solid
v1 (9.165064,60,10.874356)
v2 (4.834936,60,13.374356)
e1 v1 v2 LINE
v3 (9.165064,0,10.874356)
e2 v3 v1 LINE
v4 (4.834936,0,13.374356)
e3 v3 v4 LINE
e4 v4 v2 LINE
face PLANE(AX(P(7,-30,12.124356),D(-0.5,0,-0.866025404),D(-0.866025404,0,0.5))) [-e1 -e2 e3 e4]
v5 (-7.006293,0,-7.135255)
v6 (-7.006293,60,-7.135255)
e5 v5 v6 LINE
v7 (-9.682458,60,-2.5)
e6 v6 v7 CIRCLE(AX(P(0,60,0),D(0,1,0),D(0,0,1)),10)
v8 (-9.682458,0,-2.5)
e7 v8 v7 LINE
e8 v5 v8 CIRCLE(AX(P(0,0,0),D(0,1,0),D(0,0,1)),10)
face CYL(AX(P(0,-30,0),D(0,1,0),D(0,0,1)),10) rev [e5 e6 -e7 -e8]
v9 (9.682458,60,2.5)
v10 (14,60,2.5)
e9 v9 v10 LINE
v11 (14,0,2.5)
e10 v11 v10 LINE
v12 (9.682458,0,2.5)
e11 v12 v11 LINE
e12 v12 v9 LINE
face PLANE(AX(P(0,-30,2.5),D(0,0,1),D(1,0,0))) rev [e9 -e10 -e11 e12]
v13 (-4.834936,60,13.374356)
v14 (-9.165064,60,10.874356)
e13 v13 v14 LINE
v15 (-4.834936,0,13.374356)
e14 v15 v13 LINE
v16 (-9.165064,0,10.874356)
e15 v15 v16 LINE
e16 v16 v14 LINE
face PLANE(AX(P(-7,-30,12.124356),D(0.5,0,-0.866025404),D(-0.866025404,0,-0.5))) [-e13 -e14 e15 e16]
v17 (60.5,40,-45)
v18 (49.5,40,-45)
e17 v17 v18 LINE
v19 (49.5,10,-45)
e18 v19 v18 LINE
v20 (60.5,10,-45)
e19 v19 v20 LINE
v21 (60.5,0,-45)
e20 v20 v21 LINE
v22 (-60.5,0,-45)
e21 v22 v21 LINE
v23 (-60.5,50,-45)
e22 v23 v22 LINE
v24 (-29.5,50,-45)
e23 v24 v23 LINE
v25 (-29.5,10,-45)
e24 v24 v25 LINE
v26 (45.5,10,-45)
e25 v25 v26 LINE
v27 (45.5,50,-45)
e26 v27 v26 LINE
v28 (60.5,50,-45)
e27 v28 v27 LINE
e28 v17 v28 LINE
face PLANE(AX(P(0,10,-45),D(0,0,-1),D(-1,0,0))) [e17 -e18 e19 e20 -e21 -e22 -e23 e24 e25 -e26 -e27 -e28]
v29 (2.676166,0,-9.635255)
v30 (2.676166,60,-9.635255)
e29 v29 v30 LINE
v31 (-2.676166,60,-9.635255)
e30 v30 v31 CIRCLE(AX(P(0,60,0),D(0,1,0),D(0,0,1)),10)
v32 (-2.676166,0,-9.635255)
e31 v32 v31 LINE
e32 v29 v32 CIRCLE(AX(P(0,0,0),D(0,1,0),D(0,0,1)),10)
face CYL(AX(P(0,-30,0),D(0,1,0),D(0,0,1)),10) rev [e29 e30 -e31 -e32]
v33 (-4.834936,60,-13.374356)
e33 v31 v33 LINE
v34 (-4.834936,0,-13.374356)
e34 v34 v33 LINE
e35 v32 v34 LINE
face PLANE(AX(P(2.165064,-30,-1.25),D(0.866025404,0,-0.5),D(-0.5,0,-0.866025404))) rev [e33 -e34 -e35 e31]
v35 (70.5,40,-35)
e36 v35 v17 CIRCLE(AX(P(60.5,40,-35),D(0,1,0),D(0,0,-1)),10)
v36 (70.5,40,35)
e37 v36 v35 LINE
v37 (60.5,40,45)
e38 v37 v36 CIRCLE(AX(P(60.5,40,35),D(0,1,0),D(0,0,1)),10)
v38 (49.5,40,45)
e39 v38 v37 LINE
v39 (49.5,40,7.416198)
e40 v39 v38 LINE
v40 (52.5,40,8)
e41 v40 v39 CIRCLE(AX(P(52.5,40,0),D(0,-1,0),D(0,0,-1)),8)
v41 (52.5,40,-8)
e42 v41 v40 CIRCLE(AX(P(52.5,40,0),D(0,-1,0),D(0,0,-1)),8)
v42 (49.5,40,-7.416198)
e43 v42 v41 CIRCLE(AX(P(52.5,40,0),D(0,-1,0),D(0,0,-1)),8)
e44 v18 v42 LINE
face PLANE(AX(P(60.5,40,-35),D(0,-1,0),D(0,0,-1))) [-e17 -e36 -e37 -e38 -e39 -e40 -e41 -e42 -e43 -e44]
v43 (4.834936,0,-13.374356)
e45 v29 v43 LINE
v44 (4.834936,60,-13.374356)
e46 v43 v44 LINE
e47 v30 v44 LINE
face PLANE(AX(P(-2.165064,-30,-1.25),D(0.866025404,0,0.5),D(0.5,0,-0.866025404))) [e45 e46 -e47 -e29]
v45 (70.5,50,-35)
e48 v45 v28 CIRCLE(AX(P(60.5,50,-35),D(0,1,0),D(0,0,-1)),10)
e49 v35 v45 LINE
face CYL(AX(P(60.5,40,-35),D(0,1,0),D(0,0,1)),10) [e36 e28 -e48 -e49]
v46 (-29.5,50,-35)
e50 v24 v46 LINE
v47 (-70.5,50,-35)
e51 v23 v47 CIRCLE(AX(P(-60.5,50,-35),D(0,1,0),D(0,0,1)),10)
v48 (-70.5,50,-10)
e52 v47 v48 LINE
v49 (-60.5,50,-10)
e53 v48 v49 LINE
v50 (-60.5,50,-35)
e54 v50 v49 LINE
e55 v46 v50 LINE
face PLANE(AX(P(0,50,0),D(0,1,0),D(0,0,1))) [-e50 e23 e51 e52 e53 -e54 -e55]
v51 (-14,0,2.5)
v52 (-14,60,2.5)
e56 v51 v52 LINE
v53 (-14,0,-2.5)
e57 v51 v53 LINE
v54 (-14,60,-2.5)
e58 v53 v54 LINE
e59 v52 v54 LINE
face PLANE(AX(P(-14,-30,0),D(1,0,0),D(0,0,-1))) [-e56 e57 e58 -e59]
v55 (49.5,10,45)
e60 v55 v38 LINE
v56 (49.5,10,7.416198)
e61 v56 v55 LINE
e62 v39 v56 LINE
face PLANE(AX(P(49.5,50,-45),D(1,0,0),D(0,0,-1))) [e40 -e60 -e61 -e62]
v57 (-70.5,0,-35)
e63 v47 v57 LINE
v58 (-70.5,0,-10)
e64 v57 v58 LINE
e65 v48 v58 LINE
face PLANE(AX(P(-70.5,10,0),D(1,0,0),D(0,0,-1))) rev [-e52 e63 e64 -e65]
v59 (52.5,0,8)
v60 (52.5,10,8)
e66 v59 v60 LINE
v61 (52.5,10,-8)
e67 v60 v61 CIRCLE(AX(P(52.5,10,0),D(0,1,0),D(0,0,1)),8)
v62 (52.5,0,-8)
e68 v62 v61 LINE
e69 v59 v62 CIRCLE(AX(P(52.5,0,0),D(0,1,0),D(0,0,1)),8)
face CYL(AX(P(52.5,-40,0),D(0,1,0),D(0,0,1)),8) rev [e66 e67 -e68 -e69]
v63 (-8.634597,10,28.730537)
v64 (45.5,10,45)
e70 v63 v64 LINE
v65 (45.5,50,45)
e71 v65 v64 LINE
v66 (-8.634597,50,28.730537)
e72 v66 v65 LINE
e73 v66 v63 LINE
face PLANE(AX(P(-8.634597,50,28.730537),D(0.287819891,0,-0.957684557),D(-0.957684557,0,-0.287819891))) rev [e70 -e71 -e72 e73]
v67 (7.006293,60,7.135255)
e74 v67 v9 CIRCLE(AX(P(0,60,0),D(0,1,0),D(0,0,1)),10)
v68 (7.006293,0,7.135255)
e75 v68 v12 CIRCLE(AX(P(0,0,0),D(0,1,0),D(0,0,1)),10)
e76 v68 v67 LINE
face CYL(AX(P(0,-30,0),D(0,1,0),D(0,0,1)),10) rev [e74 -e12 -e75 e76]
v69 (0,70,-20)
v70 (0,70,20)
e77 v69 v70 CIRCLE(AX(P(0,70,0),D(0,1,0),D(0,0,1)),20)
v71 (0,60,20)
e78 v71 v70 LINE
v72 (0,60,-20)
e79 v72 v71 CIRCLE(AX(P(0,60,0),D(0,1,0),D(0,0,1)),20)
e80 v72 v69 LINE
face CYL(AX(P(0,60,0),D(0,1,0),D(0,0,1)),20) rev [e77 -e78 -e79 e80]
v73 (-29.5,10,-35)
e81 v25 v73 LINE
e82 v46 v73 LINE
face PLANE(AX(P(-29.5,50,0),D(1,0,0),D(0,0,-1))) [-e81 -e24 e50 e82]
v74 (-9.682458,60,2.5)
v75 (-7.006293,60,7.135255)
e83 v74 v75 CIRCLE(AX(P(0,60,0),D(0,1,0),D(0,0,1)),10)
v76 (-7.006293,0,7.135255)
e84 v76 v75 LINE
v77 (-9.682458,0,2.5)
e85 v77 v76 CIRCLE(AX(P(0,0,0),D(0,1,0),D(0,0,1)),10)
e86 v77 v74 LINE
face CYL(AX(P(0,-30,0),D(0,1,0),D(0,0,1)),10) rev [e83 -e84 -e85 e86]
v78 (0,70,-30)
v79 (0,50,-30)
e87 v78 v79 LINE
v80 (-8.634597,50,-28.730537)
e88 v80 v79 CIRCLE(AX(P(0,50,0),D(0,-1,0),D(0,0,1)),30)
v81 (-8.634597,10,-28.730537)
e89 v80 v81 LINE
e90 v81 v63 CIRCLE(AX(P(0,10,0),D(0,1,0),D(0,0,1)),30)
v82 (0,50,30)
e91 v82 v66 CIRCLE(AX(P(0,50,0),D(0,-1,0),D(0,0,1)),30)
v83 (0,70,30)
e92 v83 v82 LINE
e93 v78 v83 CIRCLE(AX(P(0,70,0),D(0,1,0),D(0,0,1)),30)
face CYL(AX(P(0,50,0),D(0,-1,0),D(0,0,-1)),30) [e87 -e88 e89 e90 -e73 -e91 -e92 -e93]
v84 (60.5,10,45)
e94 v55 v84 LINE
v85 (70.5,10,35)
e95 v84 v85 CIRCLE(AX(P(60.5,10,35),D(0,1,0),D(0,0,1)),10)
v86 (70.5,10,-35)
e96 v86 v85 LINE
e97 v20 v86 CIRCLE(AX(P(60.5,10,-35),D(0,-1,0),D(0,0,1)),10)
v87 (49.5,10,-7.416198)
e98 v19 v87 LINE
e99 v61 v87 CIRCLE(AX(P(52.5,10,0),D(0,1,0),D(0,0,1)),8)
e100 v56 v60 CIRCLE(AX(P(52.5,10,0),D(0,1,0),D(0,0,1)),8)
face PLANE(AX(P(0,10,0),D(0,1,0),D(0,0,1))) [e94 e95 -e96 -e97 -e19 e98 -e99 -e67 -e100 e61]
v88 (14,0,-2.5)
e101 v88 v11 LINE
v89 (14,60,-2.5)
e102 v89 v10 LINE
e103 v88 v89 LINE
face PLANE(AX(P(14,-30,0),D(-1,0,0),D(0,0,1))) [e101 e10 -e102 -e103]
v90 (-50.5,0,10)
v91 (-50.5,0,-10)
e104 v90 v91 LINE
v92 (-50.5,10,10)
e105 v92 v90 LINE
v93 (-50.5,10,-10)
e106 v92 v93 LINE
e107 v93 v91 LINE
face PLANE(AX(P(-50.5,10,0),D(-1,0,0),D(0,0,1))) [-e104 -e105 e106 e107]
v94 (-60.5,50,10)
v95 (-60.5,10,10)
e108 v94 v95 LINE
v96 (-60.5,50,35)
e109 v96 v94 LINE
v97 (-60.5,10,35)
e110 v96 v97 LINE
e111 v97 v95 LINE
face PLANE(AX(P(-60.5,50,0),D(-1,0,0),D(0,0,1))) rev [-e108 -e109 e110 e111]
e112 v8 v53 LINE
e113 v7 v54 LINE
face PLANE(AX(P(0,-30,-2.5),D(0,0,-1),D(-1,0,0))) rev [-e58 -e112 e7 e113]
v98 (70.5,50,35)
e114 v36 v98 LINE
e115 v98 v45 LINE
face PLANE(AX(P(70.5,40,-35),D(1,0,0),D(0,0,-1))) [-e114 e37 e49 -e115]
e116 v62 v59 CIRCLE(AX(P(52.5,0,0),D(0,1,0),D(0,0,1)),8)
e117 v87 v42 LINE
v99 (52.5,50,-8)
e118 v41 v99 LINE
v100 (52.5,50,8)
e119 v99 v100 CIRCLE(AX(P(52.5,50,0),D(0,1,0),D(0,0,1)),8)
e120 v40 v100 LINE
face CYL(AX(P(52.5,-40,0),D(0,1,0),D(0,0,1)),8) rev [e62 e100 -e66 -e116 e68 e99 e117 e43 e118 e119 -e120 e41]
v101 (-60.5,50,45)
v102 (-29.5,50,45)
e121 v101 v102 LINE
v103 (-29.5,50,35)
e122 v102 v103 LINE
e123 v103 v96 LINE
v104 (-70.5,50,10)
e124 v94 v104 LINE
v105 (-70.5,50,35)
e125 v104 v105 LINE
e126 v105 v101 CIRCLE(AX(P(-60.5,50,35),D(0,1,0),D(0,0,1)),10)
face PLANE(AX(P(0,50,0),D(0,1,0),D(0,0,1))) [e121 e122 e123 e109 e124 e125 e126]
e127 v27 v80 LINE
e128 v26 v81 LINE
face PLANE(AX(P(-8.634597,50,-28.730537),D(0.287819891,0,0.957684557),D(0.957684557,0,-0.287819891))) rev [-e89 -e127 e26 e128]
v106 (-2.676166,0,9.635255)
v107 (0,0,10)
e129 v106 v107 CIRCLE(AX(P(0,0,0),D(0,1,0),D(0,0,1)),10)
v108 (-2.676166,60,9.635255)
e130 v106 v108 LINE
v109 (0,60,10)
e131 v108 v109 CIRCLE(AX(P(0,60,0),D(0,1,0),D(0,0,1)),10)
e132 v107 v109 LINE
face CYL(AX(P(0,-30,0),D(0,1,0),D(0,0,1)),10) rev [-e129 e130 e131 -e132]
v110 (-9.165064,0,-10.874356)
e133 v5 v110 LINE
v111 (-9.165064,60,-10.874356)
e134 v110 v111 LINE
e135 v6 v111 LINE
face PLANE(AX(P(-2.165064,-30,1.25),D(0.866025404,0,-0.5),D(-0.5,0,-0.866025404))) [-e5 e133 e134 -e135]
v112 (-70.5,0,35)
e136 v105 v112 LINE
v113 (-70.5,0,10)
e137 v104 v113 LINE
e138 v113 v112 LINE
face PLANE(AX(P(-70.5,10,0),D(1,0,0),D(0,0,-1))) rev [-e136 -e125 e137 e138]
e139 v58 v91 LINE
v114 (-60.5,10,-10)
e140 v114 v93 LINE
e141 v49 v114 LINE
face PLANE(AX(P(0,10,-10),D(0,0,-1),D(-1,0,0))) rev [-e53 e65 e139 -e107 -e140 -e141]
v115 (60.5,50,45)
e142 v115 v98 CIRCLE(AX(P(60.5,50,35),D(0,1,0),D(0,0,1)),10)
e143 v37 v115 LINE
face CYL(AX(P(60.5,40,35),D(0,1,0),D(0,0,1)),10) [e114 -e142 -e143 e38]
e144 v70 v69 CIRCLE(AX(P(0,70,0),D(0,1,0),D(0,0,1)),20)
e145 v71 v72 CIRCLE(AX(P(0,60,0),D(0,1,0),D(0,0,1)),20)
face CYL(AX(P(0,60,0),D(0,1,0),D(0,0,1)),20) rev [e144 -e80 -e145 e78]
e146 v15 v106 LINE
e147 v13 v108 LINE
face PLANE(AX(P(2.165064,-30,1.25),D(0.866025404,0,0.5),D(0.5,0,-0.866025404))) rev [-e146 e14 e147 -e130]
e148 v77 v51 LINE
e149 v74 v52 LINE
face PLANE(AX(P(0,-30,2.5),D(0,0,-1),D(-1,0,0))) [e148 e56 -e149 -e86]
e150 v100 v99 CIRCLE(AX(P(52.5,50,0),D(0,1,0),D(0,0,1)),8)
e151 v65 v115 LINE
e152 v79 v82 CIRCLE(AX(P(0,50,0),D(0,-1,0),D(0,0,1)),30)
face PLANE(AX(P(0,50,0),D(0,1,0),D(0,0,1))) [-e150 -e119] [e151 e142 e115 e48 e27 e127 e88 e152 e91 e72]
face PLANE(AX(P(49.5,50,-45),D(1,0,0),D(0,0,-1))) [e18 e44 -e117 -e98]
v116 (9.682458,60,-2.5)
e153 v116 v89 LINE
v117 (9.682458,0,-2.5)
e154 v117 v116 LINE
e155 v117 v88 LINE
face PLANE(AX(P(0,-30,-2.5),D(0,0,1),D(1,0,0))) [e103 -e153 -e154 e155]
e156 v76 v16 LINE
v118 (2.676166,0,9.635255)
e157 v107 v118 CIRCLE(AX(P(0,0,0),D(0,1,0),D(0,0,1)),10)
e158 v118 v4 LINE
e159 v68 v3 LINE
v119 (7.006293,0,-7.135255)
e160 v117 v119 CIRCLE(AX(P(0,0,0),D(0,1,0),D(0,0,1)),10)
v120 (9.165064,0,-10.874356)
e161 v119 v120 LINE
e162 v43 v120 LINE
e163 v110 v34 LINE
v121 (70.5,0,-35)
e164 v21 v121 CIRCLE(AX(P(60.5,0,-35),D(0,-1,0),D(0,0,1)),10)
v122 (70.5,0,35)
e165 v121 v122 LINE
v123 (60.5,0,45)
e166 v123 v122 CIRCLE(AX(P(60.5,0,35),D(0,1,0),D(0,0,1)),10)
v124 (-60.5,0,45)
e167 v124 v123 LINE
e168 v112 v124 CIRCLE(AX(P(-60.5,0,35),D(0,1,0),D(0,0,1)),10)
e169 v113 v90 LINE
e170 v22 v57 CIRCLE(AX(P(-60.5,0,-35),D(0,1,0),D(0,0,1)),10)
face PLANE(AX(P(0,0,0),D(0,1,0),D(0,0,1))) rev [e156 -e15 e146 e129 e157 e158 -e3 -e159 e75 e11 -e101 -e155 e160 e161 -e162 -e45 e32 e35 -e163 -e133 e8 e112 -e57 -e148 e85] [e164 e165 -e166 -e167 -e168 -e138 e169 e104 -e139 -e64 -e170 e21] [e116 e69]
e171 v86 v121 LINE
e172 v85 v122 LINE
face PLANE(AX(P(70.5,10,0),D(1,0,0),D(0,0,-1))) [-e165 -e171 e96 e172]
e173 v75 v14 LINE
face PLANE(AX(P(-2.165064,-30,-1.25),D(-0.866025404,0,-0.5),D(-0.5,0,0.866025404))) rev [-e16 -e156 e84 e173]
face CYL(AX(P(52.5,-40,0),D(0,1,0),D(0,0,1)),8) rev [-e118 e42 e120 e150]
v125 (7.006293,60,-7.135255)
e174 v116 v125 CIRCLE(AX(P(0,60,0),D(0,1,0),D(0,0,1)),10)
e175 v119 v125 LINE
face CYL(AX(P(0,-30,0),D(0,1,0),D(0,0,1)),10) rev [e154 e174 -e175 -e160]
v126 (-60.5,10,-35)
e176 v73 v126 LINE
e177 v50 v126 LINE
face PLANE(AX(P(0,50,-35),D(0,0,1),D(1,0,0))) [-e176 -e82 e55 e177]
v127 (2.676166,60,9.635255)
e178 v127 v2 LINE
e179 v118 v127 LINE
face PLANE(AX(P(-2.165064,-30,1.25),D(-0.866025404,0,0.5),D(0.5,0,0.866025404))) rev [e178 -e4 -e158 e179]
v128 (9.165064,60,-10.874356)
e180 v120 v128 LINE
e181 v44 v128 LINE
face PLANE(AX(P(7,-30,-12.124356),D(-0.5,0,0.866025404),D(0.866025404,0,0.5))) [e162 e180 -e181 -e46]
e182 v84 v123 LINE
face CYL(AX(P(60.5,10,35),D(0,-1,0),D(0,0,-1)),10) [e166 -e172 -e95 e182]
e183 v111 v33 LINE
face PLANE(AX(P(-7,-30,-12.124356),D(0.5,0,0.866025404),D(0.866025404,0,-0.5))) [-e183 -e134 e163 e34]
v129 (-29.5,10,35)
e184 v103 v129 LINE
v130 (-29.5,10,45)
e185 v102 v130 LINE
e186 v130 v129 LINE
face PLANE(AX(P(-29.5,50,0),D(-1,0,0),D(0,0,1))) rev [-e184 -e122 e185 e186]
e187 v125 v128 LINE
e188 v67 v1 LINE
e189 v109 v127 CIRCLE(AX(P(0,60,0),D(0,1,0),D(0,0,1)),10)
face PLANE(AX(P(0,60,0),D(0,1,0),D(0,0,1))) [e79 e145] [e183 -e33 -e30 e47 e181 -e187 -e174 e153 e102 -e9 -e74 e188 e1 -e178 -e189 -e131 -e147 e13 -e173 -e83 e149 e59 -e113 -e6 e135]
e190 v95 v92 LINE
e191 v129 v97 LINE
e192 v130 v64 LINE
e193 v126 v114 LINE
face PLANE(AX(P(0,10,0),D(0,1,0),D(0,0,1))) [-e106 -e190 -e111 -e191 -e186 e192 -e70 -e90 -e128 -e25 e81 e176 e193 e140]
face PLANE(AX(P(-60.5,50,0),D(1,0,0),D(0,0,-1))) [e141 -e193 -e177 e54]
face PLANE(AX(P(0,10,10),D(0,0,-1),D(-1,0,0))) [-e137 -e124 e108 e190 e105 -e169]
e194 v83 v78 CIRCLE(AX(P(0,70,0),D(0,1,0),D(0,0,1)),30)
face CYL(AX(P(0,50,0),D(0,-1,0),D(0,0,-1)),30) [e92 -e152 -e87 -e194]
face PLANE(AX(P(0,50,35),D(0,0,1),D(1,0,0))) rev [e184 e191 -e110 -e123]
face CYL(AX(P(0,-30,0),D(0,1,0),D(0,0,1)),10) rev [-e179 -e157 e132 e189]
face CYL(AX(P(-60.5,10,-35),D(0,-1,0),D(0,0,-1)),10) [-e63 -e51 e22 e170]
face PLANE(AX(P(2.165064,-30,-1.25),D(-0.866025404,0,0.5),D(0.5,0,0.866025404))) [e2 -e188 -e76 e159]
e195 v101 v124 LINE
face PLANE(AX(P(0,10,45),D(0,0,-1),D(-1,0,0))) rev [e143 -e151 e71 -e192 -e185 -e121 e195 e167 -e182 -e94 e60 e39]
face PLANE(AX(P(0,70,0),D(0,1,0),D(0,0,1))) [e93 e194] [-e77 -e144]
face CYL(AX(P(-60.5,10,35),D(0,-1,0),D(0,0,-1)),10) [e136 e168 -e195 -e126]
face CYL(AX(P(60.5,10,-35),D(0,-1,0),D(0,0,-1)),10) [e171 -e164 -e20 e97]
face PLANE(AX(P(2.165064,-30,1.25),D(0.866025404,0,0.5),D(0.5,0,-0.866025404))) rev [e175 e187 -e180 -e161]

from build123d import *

# Parameters (mm, degrees)
BASE_PLATE_DEPTH     = 10
GUIDE_WALL_DEPTH     = 40
HUB_BLOCK_DEPTH      = 40
CLEVIS_START         = -10
CLEVIS_EAR_DEPTH     = 10
GUSSET_SKETCH_W      = 4
GUSSET_SKETCH_H      = 40
GUSSET_DEPTH         = 90
CROSS_HOLE_SKETCH_R  = 8
CROSS_HOLE_16_DEPTH  = 90
HUB_BOSS_SKETCH_R    = 30
HUB_BOSS_60_DEPTH    = 20
HUB_RECESS_SKETCH_R  = 20
HUB_RECESS_40_DEPTH  = 10
SPLINE_BORE_6X_DEPTH = 90


with BuildPart() as part:
    # Base Plate Sketch → Base Plate (new body)
    with BuildSketch(Plane(origin=(0, 0, 0), x_dir=(1, 0, 0), z_dir=(0, 1, 0))):
        with BuildLine():
            Line((-60.5, 45), (60.5, 45))
            ThreePointArc((60.5, 45), (67.571067812, 42.071067812), (70.5, 35))
            Line((70.5, 35), (70.5, -35))
            ThreePointArc((70.5, -35), (67.571067812, -42.071067812), (60.5, -45))
            Line((60.5, -45), (-60.5, -45))
            ThreePointArc((-60.5, -45), (-67.571067812, -42.071067812), (-70.5, -35))
            Line((-70.5, -35), (-70.5, -10))
            Line((-70.5, -10), (-50.5, -10))
            Line((-50.5, -10), (-50.5, 10))
            Line((-50.5, 10), (-70.5, 10))
            Line((-70.5, 10), (-70.5, 35))
            ThreePointArc((-70.5, 35), (-67.571067812, 42.071067812), (-60.5, 45))
        make_face()
    extrude(amount=BASE_PLATE_DEPTH)

    # Guide Wall Sketch → Guide Wall (add)
    with BuildSketch(Plane(origin=(0, 10, 0), x_dir=(1, 0, 0), z_dir=(0, 1, 0))):
        with BuildLine():
            Line((-29.5, 45), (-60.5, 45))
            ThreePointArc((-60.5, 45), (-67.571067812, 42.071067812), (-70.5, 35))
            Line((-70.5, 35), (-70.5, 10))
            Line((-70.5, 10), (-60.5, 10))
            Line((-60.5, 10), (-60.5, 35))
            Line((-60.5, 35), (-29.5, 35))
            Line((-29.5, 35), (-29.5, 45))
        make_face()
        with BuildLine():
            Line((-70.5, -10), (-70.5, -35))
            ThreePointArc((-70.5, -35), (-67.571067812, -42.071067812), (-60.5, -45))
            Line((-60.5, -45), (-29.5, -45))
            Line((-29.5, -45), (-29.5, -35))
            Line((-29.5, -35), (-60.5, -35))
            Line((-60.5, -35), (-60.5, -10))
            Line((-60.5, -10), (-70.5, -10))
        make_face()
    extrude(amount=GUIDE_WALL_DEPTH)

    # Hub Block Sketch → Hub Block (add)
    with BuildSketch(Plane(origin=(0, 10, 0), x_dir=(1, 0, 0), z_dir=(0, 1, 0))):
        with BuildLine():
            Line((45.5, -45), (45.5, 45))
            Line((45.5, 45), (-8.634596738, 28.730536702))
            ThreePointArc((-8.634596738, 28.730536702), (-30, 0), (-8.634596738, -28.730536702))
            Line((-8.634596738, -28.730536702), (45.5, -45))
        make_face()
    extrude(amount=HUB_BLOCK_DEPTH)

    # Clevis Ear Sketch → Clevis Ear (add)
    with BuildSketch(Plane(origin=(0, 50, 0), x_dir=(1, 0, 0), z_dir=(0, 1, 0)).offset(CLEVIS_START)):
        with BuildLine():
            Line((45.5, 45), (60.5, 45))
            ThreePointArc((60.5, 45), (67.571067812, 42.071067812), (70.5, 35))
            Line((70.5, 35), (70.5, -35))
            ThreePointArc((70.5, -35), (67.571067812, -42.071067812), (60.5, -45))
            Line((60.5, -45), (45.5, -45))
            Line((45.5, -45), (45.5, 45))
        make_face()
    extrude(amount=CLEVIS_EAR_DEPTH)

    # Gusset Sketch → Gusset (add)
    with BuildSketch(Plane.XY.offset(45)):
        with Locations((47.5, 30)):
            Rectangle(GUSSET_SKETCH_W, GUSSET_SKETCH_H)
    extrude(amount=-GUSSET_DEPTH)

    # Cross Hole Sketch → Cross Hole Ø16 (cut)
    with BuildSketch(Plane(origin=(0, 50, 0), x_dir=(1, 0, 0), z_dir=(0, 1, 0))):
        with Locations(Location((52.5, 0, 0), (0, 0, 270))):
            Circle(CROSS_HOLE_SKETCH_R)
    extrude(amount=-CROSS_HOLE_16_DEPTH, mode=Mode.SUBTRACT)

    # Hub Boss Sketch → Hub Boss Ø60 (add)
    with BuildSketch(Plane(origin=(0, 50, 0), x_dir=(1, 0, 0), z_dir=(0, 1, 0))):
        with Locations(Location((0, 0, 0), (0, 0, 106.727481019))):
            Circle(HUB_BOSS_SKETCH_R)
    extrude(amount=HUB_BOSS_60_DEPTH)

    # Hub Recess Sketch → Hub Recess Ø40 (cut)
    with BuildSketch(Plane(origin=(0, 70, 0), x_dir=(1, 0, 0), z_dir=(0, 1, 0))):
        with Locations(Location((0, 0, 0), (0, 0, 270))):
            Circle(HUB_RECESS_SKETCH_R)
    extrude(amount=-HUB_RECESS_40_DEPTH, mode=Mode.SUBTRACT)

    # Spline Bore Sketch → Spline Bore 6x (cut)
    with BuildSketch(Plane(origin=(0, 60, 0), x_dir=(1, 0, 0), z_dir=(0, 1, 0))):
        with BuildLine():
            Line((-3.703283788, -11.414275675), (-2.676165673, -9.635254916))
            ThreePointArc((-2.676165673, -9.635254916), (0, -10), (2.676165673, -9.635254916))
            Line((2.676165673, -9.635254916), (3.703283788, -11.414275675))
            Line((3.703283788, -11.414275675), (4.834936491, -13.374355653))
            Line((4.834936491, -13.374355653), (9.165063509, -10.874355653))
            Line((9.165063509, -10.874355653), (8.033410807, -8.914275675))
            Line((8.033410807, -8.914275675), (7.006292692, -7.135254916))
            ThreePointArc((7.006292692, -7.135254916), (8.660254038, -5), (9.682458366, -2.5))
            Line((9.682458366, -2.5), (11.736694594, -2.5))
            Line((11.736694594, -2.5), (14, -2.5))
            Line((14, -2.5), (14, 2.5))
            Line((14, 2.5), (11.736694594, 2.5))
            Line((11.736694594, 2.5), (9.682458366, 2.5))
            ThreePointArc((9.682458366, 2.5), (8.660254038, 5), (7.006292692, 7.135254916))
            Line((7.006292692, 7.135254916), (8.033410807, 8.914275675))
            Line((8.033410807, 8.914275675), (9.165063509, 10.874355653))
            Line((9.165063509, 10.874355653), (4.834936491, 13.374355653))
            Line((4.834936491, 13.374355653), (3.703283788, 11.414275675))
            Line((3.703283788, 11.414275675), (2.676165673, 9.635254916))
            ThreePointArc((2.676165673, 9.635254916), (0, 10), (-2.676165673, 9.635254916))
            Line((-2.676165673, 9.635254916), (-3.703283788, 11.414275675))
            Line((-3.703283788, 11.414275675), (-4.834936491, 13.374355653))
            Line((-4.834936491, 13.374355653), (-9.165063509, 10.874355653))
            Line((-9.165063509, 10.874355653), (-8.033410807, 8.914275675))
            Line((-8.033410807, 8.914275675), (-7.006292692, 7.135254916))
            ThreePointArc((-7.006292692, 7.135254916), (-8.660254038, 5), (-9.682458366, 2.5))
            Line((-9.682458366, 2.5), (-11.736694594, 2.5))
            Line((-11.736694594, 2.5), (-14, 2.5))
            Line((-14, 2.5), (-14, -2.5))
            Line((-14, -2.5), (-11.736694594, -2.5))
            Line((-11.736694594, -2.5), (-9.682458366, -2.5))
            ThreePointArc((-9.682458366, -2.5), (-8.660254038, -5), (-7.006292692, -7.135254916))
            Line((-7.006292692, -7.135254916), (-8.033410807, -8.914275675))
            Line((-8.033410807, -8.914275675), (-9.165063509, -10.874355653))
            Line((-9.165063509, -10.874355653), (-4.834936491, -13.374355653))
            Line((-4.834936491, -13.374355653), (-3.703283788, -11.414275675))
        make_face()
    extrude(amount=-SPLINE_BORE_6X_DEPTH, mode=Mode.SUBTRACT)


solid = part.part
